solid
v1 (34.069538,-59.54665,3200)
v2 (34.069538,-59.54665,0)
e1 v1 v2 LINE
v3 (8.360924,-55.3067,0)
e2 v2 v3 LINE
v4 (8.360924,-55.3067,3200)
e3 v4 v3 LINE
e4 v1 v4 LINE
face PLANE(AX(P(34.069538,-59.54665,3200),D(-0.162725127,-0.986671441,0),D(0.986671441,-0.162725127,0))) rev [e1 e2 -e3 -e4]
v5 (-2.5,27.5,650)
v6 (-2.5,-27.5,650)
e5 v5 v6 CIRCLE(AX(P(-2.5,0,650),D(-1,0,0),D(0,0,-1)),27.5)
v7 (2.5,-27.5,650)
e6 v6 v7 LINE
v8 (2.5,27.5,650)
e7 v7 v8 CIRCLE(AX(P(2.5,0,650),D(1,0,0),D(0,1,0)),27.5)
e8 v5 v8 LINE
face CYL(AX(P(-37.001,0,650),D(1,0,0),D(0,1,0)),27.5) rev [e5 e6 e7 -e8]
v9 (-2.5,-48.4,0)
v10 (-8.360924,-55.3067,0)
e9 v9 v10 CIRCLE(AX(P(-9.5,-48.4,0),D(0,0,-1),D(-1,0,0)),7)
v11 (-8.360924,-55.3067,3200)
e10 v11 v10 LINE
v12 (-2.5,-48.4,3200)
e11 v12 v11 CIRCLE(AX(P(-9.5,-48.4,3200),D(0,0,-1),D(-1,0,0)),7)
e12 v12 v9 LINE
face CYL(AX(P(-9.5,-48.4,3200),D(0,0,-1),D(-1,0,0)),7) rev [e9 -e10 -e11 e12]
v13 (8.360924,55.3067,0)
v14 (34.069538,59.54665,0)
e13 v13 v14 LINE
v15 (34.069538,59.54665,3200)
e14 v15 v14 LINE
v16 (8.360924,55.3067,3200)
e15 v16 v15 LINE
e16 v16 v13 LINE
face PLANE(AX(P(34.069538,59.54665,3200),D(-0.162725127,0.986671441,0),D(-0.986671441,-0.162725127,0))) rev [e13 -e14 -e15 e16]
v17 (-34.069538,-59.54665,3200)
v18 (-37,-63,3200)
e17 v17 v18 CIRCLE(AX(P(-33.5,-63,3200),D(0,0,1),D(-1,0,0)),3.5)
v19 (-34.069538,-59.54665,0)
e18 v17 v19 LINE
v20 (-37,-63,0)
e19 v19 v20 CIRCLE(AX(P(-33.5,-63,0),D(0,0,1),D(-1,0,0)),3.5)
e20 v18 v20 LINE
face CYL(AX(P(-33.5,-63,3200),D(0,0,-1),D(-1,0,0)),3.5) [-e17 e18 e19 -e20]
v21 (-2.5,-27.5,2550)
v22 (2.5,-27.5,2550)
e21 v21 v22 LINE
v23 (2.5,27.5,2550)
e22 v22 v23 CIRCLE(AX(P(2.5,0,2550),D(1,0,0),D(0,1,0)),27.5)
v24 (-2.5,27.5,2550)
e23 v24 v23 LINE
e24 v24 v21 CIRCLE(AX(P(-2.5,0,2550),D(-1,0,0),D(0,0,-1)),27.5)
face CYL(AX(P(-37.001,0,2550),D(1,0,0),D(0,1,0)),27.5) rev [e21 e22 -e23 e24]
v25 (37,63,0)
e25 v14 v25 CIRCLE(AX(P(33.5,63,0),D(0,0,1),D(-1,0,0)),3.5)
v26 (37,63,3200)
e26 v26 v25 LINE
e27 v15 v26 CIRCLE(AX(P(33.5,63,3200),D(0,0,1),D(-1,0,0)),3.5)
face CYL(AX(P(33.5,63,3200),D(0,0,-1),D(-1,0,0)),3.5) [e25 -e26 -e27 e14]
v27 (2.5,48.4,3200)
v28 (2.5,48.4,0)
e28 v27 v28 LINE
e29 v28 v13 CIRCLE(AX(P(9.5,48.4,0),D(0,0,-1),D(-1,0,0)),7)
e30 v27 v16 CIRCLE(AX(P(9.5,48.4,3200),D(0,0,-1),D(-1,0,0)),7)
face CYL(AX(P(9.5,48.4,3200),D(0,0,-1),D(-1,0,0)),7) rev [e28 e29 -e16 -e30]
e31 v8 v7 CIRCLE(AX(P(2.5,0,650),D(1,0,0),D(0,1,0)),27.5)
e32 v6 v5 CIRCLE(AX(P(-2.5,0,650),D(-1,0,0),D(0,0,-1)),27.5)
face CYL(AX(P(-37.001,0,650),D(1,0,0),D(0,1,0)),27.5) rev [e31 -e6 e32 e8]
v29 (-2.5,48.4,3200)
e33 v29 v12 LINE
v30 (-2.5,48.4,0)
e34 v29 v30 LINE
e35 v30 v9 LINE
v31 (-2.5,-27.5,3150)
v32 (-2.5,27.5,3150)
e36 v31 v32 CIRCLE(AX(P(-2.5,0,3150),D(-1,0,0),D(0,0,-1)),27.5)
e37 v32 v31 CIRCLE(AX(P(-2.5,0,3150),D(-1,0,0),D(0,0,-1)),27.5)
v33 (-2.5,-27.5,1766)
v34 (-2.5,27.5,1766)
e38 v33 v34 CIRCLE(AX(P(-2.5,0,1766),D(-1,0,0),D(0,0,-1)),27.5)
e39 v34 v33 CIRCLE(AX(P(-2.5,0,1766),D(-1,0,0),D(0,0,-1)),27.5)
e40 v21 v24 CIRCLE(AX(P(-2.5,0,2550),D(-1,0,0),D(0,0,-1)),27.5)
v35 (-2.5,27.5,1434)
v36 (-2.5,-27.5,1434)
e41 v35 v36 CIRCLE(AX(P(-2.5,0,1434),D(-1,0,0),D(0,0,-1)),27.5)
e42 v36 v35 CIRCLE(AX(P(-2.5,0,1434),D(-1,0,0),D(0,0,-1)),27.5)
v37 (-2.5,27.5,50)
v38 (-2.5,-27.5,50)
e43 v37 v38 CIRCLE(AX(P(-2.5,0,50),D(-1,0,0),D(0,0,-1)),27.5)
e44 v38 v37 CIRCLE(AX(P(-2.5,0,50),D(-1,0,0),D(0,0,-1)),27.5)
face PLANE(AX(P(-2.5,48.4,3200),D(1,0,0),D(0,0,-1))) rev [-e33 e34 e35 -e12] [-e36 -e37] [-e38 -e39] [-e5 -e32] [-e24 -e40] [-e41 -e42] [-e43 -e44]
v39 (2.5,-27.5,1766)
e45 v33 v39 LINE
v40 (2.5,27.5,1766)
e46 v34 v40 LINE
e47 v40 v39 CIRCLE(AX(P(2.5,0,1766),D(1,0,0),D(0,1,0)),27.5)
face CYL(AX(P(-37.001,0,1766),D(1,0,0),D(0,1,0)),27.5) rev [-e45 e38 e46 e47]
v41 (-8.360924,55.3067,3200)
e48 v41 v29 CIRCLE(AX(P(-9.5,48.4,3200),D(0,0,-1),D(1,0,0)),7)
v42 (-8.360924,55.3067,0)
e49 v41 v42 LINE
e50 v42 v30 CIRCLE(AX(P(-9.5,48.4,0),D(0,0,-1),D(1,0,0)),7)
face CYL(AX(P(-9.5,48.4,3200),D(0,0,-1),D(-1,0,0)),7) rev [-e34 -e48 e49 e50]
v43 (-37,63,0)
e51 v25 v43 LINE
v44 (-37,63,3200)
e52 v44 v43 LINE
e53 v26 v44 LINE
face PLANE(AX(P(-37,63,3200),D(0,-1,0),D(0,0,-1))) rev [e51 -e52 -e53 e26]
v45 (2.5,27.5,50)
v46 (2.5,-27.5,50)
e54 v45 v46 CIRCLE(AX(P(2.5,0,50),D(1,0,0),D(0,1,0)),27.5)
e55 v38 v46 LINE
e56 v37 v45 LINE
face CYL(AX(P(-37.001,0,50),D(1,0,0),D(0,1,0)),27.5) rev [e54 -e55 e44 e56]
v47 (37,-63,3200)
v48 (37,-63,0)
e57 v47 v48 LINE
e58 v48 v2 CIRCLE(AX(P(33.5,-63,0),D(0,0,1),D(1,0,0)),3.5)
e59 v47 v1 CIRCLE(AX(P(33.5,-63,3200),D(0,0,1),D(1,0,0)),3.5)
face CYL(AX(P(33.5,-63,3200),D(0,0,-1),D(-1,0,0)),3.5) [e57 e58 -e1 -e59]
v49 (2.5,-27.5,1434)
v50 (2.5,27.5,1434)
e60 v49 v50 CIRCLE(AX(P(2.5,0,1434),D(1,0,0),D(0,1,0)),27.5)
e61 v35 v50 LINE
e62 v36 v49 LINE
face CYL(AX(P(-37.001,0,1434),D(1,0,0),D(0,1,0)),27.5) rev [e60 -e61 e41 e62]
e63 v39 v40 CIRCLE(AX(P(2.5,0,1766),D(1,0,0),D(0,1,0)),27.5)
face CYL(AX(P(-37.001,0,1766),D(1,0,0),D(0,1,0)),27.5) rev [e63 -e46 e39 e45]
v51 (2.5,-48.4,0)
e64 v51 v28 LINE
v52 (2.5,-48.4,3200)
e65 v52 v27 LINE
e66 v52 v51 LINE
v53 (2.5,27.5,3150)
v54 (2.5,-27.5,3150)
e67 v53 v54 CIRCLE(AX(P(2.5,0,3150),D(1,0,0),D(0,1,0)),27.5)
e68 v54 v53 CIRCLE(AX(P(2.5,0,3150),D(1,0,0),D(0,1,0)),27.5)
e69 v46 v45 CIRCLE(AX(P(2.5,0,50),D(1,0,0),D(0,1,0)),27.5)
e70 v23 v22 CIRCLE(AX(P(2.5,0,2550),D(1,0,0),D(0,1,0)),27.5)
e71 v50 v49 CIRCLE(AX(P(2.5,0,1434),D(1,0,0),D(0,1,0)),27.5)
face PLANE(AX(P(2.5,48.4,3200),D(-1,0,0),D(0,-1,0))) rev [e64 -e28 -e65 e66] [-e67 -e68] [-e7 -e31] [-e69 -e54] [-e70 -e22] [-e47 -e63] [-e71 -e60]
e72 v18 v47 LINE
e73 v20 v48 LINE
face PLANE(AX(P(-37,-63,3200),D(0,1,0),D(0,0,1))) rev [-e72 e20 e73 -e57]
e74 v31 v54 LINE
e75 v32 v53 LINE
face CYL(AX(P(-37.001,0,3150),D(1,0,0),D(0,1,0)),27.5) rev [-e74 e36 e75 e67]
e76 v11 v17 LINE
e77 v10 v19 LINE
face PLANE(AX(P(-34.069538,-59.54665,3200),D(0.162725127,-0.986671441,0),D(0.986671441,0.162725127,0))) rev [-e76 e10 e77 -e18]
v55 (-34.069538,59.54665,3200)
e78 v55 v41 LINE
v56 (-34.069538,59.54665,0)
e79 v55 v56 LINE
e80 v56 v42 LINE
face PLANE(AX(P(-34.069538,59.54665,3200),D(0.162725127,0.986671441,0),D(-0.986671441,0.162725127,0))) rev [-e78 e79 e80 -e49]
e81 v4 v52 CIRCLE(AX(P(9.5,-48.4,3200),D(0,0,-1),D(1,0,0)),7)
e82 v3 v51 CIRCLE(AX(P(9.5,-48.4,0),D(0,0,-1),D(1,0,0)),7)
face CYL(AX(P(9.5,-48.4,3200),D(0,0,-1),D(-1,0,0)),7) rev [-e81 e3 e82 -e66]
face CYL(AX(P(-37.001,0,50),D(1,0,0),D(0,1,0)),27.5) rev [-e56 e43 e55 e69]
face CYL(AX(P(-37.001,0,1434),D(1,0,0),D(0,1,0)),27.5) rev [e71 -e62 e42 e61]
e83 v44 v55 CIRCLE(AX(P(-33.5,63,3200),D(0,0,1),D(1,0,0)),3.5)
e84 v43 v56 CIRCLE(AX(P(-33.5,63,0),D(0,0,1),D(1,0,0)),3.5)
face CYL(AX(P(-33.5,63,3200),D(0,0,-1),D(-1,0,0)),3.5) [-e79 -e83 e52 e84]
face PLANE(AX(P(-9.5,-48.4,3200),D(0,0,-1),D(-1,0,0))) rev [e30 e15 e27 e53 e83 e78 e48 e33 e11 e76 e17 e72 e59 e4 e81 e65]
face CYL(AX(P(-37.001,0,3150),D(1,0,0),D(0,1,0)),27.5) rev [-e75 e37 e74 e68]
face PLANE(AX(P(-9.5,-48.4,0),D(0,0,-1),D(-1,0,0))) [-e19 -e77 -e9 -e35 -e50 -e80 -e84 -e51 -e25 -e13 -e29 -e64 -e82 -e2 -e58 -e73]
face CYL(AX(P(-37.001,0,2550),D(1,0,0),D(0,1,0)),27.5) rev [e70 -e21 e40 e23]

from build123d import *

# Parameters (mm, degrees)
BOSS_EXTRUDE1_DEPTH = 3200
CUT_EXTRUDE1_REACH  = 3202.864
SKETCH2_R           = 27.5


with BuildPart() as part:
    # Sketch1 → Boss-Extrude1 (new body)
    with BuildSketch(Plane.XY):
        with BuildLine():
            Line((-2.5, 48.4), (-2.5, -48.4))
            ThreePointArc((-2.5, -48.4), (-4.162700532, -52.929153828), (-8.360924112, -55.306700089))
            Line((-8.360924112, -55.306700089), (-34.069537944, -59.546649955))
            ThreePointArc((-34.069537944, -59.546649955), (-36.168649734, -60.735423086), (-37, -63))
            Line((-37, -63), (37, -63))
            ThreePointArc((37, -63), (36.168649734, -60.735423086), (34.069537944, -59.546649955))
            Line((34.069537944, -59.546649955), (8.360924112, -55.306700089))
            ThreePointArc((8.360924112, -55.306700089), (4.162700532, -52.929153828), (2.5, -48.4))
            Line((2.5, -48.4), (2.5, 48.4))
            ThreePointArc((2.5, 48.4), (4.162700532, 52.929153828), (8.360924112, 55.306700089))
            Line((8.360924112, 55.306700089), (34.069537944, 59.546649955))
            ThreePointArc((34.069537944, 59.546649955), (36.168649734, 60.735423086), (37, 63))
            Line((37, 63), (-37, 63))
            ThreePointArc((-37, 63), (-36.168649734, 60.735423086), (-34.069537944, 59.546649955))
            Line((-34.069537944, 59.546649955), (-8.360924112, 55.306700089))
            ThreePointArc((-8.360924112, 55.306700089), (-4.162700532, 52.929153828), (-2.5, 48.4))
        make_face()
    extrude(amount=BOSS_EXTRUDE1_DEPTH)

    # Sketch2 → Cut-Extrude1 (cut, up to next)
    with BuildSketch(Plane(origin=(2.5, 0, 0), x_dir=(0, 0, -1), z_dir=(1, 0, 0)), mode=Mode.PRIVATE) as cut_extrude1_sk1:
        with Locations(Location((-50, 0, 0), (0, 0, 90))):
            Circle(SKETCH2_R)
    cut_extrude1_tool1 = extrude(cut_extrude1_sk1.sketch, amount=-CUT_EXTRUDE1_REACH, mode=Mode.PRIVATE) & part.part
    # Sketch2 → Cut-Extrude1 (cut, up to next)
    with BuildSketch(Plane(origin=(2.5, 0, 0), x_dir=(0, 0, -1), z_dir=(1, 0, 0)), mode=Mode.PRIVATE) as cut_extrude1_sk2:
        with Locations(Location((-650, 0, 0), (0, 0, 90))):
            Circle(SKETCH2_R)
    cut_extrude1_tool2 = extrude(cut_extrude1_sk2.sketch, amount=-CUT_EXTRUDE1_REACH, mode=Mode.PRIVATE) & part.part
    # Sketch2 → Cut-Extrude1 (cut, up to next)
    with BuildSketch(Plane(origin=(2.5, 0, 0), x_dir=(0, 0, -1), z_dir=(1, 0, 0)), mode=Mode.PRIVATE) as cut_extrude1_sk3:
        with Locations(Location((-1434, 0, 0), (0, 0, 90))):
            Circle(SKETCH2_R)
    cut_extrude1_tool3 = extrude(cut_extrude1_sk3.sketch, amount=-CUT_EXTRUDE1_REACH, mode=Mode.PRIVATE) & part.part
    # Sketch2 → Cut-Extrude1 (cut, up to next)
    with BuildSketch(Plane(origin=(2.5, 0, 0), x_dir=(0, 0, -1), z_dir=(1, 0, 0)), mode=Mode.PRIVATE) as cut_extrude1_sk4:
        with Locations(Location((-1766, 0, 0), (0, 0, 90))):
            Circle(SKETCH2_R)
    cut_extrude1_tool4 = extrude(cut_extrude1_sk4.sketch, amount=-CUT_EXTRUDE1_REACH, mode=Mode.PRIVATE) & part.part
    # Sketch2 → Cut-Extrude1 (cut, up to next)
    with BuildSketch(Plane(origin=(2.5, 0, 0), x_dir=(0, 0, -1), z_dir=(1, 0, 0)), mode=Mode.PRIVATE) as cut_extrude1_sk5:
        with Locations(Location((-2550, 0, 0), (0, 0, 90))):
            Circle(SKETCH2_R)
    cut_extrude1_tool5 = extrude(cut_extrude1_sk5.sketch, amount=-CUT_EXTRUDE1_REACH, mode=Mode.PRIVATE) & part.part
    # Sketch2 → Cut-Extrude1 (cut, up to next)
    with BuildSketch(Plane(origin=(2.5, 0, 0), x_dir=(0, 0, -1), z_dir=(1, 0, 0)), mode=Mode.PRIVATE) as cut_extrude1_sk6:
        with Locations(Location((-3150, 0, 0), (0, 0, 90))):
            Circle(SKETCH2_R)
    cut_extrude1_tool6 = extrude(cut_extrude1_sk6.sketch, amount=-CUT_EXTRUDE1_REACH, mode=Mode.PRIVATE) & part.part
    add(cut_extrude1_tool1.solids().sort_by_distance((2.5, 0, 50))[0], mode=Mode.SUBTRACT)
    add(cut_extrude1_tool2.solids().sort_by_distance((2.5, 0, 650))[0], mode=Mode.SUBTRACT)
    add(cut_extrude1_tool3.solids().sort_by_distance((2.5, 0, 1434))[0], mode=Mode.SUBTRACT)
    add(cut_extrude1_tool4.solids().sort_by_distance((2.5, 0, 1766))[0], mode=Mode.SUBTRACT)
    add(cut_extrude1_tool5.solids().sort_by_distance((2.5, 0, 2550))[0], mode=Mode.SUBTRACT)
    add(cut_extrude1_tool6.solids().sort_by_distance((2.5, 0, 3150))[0], mode=Mode.SUBTRACT)


solid = part.part
